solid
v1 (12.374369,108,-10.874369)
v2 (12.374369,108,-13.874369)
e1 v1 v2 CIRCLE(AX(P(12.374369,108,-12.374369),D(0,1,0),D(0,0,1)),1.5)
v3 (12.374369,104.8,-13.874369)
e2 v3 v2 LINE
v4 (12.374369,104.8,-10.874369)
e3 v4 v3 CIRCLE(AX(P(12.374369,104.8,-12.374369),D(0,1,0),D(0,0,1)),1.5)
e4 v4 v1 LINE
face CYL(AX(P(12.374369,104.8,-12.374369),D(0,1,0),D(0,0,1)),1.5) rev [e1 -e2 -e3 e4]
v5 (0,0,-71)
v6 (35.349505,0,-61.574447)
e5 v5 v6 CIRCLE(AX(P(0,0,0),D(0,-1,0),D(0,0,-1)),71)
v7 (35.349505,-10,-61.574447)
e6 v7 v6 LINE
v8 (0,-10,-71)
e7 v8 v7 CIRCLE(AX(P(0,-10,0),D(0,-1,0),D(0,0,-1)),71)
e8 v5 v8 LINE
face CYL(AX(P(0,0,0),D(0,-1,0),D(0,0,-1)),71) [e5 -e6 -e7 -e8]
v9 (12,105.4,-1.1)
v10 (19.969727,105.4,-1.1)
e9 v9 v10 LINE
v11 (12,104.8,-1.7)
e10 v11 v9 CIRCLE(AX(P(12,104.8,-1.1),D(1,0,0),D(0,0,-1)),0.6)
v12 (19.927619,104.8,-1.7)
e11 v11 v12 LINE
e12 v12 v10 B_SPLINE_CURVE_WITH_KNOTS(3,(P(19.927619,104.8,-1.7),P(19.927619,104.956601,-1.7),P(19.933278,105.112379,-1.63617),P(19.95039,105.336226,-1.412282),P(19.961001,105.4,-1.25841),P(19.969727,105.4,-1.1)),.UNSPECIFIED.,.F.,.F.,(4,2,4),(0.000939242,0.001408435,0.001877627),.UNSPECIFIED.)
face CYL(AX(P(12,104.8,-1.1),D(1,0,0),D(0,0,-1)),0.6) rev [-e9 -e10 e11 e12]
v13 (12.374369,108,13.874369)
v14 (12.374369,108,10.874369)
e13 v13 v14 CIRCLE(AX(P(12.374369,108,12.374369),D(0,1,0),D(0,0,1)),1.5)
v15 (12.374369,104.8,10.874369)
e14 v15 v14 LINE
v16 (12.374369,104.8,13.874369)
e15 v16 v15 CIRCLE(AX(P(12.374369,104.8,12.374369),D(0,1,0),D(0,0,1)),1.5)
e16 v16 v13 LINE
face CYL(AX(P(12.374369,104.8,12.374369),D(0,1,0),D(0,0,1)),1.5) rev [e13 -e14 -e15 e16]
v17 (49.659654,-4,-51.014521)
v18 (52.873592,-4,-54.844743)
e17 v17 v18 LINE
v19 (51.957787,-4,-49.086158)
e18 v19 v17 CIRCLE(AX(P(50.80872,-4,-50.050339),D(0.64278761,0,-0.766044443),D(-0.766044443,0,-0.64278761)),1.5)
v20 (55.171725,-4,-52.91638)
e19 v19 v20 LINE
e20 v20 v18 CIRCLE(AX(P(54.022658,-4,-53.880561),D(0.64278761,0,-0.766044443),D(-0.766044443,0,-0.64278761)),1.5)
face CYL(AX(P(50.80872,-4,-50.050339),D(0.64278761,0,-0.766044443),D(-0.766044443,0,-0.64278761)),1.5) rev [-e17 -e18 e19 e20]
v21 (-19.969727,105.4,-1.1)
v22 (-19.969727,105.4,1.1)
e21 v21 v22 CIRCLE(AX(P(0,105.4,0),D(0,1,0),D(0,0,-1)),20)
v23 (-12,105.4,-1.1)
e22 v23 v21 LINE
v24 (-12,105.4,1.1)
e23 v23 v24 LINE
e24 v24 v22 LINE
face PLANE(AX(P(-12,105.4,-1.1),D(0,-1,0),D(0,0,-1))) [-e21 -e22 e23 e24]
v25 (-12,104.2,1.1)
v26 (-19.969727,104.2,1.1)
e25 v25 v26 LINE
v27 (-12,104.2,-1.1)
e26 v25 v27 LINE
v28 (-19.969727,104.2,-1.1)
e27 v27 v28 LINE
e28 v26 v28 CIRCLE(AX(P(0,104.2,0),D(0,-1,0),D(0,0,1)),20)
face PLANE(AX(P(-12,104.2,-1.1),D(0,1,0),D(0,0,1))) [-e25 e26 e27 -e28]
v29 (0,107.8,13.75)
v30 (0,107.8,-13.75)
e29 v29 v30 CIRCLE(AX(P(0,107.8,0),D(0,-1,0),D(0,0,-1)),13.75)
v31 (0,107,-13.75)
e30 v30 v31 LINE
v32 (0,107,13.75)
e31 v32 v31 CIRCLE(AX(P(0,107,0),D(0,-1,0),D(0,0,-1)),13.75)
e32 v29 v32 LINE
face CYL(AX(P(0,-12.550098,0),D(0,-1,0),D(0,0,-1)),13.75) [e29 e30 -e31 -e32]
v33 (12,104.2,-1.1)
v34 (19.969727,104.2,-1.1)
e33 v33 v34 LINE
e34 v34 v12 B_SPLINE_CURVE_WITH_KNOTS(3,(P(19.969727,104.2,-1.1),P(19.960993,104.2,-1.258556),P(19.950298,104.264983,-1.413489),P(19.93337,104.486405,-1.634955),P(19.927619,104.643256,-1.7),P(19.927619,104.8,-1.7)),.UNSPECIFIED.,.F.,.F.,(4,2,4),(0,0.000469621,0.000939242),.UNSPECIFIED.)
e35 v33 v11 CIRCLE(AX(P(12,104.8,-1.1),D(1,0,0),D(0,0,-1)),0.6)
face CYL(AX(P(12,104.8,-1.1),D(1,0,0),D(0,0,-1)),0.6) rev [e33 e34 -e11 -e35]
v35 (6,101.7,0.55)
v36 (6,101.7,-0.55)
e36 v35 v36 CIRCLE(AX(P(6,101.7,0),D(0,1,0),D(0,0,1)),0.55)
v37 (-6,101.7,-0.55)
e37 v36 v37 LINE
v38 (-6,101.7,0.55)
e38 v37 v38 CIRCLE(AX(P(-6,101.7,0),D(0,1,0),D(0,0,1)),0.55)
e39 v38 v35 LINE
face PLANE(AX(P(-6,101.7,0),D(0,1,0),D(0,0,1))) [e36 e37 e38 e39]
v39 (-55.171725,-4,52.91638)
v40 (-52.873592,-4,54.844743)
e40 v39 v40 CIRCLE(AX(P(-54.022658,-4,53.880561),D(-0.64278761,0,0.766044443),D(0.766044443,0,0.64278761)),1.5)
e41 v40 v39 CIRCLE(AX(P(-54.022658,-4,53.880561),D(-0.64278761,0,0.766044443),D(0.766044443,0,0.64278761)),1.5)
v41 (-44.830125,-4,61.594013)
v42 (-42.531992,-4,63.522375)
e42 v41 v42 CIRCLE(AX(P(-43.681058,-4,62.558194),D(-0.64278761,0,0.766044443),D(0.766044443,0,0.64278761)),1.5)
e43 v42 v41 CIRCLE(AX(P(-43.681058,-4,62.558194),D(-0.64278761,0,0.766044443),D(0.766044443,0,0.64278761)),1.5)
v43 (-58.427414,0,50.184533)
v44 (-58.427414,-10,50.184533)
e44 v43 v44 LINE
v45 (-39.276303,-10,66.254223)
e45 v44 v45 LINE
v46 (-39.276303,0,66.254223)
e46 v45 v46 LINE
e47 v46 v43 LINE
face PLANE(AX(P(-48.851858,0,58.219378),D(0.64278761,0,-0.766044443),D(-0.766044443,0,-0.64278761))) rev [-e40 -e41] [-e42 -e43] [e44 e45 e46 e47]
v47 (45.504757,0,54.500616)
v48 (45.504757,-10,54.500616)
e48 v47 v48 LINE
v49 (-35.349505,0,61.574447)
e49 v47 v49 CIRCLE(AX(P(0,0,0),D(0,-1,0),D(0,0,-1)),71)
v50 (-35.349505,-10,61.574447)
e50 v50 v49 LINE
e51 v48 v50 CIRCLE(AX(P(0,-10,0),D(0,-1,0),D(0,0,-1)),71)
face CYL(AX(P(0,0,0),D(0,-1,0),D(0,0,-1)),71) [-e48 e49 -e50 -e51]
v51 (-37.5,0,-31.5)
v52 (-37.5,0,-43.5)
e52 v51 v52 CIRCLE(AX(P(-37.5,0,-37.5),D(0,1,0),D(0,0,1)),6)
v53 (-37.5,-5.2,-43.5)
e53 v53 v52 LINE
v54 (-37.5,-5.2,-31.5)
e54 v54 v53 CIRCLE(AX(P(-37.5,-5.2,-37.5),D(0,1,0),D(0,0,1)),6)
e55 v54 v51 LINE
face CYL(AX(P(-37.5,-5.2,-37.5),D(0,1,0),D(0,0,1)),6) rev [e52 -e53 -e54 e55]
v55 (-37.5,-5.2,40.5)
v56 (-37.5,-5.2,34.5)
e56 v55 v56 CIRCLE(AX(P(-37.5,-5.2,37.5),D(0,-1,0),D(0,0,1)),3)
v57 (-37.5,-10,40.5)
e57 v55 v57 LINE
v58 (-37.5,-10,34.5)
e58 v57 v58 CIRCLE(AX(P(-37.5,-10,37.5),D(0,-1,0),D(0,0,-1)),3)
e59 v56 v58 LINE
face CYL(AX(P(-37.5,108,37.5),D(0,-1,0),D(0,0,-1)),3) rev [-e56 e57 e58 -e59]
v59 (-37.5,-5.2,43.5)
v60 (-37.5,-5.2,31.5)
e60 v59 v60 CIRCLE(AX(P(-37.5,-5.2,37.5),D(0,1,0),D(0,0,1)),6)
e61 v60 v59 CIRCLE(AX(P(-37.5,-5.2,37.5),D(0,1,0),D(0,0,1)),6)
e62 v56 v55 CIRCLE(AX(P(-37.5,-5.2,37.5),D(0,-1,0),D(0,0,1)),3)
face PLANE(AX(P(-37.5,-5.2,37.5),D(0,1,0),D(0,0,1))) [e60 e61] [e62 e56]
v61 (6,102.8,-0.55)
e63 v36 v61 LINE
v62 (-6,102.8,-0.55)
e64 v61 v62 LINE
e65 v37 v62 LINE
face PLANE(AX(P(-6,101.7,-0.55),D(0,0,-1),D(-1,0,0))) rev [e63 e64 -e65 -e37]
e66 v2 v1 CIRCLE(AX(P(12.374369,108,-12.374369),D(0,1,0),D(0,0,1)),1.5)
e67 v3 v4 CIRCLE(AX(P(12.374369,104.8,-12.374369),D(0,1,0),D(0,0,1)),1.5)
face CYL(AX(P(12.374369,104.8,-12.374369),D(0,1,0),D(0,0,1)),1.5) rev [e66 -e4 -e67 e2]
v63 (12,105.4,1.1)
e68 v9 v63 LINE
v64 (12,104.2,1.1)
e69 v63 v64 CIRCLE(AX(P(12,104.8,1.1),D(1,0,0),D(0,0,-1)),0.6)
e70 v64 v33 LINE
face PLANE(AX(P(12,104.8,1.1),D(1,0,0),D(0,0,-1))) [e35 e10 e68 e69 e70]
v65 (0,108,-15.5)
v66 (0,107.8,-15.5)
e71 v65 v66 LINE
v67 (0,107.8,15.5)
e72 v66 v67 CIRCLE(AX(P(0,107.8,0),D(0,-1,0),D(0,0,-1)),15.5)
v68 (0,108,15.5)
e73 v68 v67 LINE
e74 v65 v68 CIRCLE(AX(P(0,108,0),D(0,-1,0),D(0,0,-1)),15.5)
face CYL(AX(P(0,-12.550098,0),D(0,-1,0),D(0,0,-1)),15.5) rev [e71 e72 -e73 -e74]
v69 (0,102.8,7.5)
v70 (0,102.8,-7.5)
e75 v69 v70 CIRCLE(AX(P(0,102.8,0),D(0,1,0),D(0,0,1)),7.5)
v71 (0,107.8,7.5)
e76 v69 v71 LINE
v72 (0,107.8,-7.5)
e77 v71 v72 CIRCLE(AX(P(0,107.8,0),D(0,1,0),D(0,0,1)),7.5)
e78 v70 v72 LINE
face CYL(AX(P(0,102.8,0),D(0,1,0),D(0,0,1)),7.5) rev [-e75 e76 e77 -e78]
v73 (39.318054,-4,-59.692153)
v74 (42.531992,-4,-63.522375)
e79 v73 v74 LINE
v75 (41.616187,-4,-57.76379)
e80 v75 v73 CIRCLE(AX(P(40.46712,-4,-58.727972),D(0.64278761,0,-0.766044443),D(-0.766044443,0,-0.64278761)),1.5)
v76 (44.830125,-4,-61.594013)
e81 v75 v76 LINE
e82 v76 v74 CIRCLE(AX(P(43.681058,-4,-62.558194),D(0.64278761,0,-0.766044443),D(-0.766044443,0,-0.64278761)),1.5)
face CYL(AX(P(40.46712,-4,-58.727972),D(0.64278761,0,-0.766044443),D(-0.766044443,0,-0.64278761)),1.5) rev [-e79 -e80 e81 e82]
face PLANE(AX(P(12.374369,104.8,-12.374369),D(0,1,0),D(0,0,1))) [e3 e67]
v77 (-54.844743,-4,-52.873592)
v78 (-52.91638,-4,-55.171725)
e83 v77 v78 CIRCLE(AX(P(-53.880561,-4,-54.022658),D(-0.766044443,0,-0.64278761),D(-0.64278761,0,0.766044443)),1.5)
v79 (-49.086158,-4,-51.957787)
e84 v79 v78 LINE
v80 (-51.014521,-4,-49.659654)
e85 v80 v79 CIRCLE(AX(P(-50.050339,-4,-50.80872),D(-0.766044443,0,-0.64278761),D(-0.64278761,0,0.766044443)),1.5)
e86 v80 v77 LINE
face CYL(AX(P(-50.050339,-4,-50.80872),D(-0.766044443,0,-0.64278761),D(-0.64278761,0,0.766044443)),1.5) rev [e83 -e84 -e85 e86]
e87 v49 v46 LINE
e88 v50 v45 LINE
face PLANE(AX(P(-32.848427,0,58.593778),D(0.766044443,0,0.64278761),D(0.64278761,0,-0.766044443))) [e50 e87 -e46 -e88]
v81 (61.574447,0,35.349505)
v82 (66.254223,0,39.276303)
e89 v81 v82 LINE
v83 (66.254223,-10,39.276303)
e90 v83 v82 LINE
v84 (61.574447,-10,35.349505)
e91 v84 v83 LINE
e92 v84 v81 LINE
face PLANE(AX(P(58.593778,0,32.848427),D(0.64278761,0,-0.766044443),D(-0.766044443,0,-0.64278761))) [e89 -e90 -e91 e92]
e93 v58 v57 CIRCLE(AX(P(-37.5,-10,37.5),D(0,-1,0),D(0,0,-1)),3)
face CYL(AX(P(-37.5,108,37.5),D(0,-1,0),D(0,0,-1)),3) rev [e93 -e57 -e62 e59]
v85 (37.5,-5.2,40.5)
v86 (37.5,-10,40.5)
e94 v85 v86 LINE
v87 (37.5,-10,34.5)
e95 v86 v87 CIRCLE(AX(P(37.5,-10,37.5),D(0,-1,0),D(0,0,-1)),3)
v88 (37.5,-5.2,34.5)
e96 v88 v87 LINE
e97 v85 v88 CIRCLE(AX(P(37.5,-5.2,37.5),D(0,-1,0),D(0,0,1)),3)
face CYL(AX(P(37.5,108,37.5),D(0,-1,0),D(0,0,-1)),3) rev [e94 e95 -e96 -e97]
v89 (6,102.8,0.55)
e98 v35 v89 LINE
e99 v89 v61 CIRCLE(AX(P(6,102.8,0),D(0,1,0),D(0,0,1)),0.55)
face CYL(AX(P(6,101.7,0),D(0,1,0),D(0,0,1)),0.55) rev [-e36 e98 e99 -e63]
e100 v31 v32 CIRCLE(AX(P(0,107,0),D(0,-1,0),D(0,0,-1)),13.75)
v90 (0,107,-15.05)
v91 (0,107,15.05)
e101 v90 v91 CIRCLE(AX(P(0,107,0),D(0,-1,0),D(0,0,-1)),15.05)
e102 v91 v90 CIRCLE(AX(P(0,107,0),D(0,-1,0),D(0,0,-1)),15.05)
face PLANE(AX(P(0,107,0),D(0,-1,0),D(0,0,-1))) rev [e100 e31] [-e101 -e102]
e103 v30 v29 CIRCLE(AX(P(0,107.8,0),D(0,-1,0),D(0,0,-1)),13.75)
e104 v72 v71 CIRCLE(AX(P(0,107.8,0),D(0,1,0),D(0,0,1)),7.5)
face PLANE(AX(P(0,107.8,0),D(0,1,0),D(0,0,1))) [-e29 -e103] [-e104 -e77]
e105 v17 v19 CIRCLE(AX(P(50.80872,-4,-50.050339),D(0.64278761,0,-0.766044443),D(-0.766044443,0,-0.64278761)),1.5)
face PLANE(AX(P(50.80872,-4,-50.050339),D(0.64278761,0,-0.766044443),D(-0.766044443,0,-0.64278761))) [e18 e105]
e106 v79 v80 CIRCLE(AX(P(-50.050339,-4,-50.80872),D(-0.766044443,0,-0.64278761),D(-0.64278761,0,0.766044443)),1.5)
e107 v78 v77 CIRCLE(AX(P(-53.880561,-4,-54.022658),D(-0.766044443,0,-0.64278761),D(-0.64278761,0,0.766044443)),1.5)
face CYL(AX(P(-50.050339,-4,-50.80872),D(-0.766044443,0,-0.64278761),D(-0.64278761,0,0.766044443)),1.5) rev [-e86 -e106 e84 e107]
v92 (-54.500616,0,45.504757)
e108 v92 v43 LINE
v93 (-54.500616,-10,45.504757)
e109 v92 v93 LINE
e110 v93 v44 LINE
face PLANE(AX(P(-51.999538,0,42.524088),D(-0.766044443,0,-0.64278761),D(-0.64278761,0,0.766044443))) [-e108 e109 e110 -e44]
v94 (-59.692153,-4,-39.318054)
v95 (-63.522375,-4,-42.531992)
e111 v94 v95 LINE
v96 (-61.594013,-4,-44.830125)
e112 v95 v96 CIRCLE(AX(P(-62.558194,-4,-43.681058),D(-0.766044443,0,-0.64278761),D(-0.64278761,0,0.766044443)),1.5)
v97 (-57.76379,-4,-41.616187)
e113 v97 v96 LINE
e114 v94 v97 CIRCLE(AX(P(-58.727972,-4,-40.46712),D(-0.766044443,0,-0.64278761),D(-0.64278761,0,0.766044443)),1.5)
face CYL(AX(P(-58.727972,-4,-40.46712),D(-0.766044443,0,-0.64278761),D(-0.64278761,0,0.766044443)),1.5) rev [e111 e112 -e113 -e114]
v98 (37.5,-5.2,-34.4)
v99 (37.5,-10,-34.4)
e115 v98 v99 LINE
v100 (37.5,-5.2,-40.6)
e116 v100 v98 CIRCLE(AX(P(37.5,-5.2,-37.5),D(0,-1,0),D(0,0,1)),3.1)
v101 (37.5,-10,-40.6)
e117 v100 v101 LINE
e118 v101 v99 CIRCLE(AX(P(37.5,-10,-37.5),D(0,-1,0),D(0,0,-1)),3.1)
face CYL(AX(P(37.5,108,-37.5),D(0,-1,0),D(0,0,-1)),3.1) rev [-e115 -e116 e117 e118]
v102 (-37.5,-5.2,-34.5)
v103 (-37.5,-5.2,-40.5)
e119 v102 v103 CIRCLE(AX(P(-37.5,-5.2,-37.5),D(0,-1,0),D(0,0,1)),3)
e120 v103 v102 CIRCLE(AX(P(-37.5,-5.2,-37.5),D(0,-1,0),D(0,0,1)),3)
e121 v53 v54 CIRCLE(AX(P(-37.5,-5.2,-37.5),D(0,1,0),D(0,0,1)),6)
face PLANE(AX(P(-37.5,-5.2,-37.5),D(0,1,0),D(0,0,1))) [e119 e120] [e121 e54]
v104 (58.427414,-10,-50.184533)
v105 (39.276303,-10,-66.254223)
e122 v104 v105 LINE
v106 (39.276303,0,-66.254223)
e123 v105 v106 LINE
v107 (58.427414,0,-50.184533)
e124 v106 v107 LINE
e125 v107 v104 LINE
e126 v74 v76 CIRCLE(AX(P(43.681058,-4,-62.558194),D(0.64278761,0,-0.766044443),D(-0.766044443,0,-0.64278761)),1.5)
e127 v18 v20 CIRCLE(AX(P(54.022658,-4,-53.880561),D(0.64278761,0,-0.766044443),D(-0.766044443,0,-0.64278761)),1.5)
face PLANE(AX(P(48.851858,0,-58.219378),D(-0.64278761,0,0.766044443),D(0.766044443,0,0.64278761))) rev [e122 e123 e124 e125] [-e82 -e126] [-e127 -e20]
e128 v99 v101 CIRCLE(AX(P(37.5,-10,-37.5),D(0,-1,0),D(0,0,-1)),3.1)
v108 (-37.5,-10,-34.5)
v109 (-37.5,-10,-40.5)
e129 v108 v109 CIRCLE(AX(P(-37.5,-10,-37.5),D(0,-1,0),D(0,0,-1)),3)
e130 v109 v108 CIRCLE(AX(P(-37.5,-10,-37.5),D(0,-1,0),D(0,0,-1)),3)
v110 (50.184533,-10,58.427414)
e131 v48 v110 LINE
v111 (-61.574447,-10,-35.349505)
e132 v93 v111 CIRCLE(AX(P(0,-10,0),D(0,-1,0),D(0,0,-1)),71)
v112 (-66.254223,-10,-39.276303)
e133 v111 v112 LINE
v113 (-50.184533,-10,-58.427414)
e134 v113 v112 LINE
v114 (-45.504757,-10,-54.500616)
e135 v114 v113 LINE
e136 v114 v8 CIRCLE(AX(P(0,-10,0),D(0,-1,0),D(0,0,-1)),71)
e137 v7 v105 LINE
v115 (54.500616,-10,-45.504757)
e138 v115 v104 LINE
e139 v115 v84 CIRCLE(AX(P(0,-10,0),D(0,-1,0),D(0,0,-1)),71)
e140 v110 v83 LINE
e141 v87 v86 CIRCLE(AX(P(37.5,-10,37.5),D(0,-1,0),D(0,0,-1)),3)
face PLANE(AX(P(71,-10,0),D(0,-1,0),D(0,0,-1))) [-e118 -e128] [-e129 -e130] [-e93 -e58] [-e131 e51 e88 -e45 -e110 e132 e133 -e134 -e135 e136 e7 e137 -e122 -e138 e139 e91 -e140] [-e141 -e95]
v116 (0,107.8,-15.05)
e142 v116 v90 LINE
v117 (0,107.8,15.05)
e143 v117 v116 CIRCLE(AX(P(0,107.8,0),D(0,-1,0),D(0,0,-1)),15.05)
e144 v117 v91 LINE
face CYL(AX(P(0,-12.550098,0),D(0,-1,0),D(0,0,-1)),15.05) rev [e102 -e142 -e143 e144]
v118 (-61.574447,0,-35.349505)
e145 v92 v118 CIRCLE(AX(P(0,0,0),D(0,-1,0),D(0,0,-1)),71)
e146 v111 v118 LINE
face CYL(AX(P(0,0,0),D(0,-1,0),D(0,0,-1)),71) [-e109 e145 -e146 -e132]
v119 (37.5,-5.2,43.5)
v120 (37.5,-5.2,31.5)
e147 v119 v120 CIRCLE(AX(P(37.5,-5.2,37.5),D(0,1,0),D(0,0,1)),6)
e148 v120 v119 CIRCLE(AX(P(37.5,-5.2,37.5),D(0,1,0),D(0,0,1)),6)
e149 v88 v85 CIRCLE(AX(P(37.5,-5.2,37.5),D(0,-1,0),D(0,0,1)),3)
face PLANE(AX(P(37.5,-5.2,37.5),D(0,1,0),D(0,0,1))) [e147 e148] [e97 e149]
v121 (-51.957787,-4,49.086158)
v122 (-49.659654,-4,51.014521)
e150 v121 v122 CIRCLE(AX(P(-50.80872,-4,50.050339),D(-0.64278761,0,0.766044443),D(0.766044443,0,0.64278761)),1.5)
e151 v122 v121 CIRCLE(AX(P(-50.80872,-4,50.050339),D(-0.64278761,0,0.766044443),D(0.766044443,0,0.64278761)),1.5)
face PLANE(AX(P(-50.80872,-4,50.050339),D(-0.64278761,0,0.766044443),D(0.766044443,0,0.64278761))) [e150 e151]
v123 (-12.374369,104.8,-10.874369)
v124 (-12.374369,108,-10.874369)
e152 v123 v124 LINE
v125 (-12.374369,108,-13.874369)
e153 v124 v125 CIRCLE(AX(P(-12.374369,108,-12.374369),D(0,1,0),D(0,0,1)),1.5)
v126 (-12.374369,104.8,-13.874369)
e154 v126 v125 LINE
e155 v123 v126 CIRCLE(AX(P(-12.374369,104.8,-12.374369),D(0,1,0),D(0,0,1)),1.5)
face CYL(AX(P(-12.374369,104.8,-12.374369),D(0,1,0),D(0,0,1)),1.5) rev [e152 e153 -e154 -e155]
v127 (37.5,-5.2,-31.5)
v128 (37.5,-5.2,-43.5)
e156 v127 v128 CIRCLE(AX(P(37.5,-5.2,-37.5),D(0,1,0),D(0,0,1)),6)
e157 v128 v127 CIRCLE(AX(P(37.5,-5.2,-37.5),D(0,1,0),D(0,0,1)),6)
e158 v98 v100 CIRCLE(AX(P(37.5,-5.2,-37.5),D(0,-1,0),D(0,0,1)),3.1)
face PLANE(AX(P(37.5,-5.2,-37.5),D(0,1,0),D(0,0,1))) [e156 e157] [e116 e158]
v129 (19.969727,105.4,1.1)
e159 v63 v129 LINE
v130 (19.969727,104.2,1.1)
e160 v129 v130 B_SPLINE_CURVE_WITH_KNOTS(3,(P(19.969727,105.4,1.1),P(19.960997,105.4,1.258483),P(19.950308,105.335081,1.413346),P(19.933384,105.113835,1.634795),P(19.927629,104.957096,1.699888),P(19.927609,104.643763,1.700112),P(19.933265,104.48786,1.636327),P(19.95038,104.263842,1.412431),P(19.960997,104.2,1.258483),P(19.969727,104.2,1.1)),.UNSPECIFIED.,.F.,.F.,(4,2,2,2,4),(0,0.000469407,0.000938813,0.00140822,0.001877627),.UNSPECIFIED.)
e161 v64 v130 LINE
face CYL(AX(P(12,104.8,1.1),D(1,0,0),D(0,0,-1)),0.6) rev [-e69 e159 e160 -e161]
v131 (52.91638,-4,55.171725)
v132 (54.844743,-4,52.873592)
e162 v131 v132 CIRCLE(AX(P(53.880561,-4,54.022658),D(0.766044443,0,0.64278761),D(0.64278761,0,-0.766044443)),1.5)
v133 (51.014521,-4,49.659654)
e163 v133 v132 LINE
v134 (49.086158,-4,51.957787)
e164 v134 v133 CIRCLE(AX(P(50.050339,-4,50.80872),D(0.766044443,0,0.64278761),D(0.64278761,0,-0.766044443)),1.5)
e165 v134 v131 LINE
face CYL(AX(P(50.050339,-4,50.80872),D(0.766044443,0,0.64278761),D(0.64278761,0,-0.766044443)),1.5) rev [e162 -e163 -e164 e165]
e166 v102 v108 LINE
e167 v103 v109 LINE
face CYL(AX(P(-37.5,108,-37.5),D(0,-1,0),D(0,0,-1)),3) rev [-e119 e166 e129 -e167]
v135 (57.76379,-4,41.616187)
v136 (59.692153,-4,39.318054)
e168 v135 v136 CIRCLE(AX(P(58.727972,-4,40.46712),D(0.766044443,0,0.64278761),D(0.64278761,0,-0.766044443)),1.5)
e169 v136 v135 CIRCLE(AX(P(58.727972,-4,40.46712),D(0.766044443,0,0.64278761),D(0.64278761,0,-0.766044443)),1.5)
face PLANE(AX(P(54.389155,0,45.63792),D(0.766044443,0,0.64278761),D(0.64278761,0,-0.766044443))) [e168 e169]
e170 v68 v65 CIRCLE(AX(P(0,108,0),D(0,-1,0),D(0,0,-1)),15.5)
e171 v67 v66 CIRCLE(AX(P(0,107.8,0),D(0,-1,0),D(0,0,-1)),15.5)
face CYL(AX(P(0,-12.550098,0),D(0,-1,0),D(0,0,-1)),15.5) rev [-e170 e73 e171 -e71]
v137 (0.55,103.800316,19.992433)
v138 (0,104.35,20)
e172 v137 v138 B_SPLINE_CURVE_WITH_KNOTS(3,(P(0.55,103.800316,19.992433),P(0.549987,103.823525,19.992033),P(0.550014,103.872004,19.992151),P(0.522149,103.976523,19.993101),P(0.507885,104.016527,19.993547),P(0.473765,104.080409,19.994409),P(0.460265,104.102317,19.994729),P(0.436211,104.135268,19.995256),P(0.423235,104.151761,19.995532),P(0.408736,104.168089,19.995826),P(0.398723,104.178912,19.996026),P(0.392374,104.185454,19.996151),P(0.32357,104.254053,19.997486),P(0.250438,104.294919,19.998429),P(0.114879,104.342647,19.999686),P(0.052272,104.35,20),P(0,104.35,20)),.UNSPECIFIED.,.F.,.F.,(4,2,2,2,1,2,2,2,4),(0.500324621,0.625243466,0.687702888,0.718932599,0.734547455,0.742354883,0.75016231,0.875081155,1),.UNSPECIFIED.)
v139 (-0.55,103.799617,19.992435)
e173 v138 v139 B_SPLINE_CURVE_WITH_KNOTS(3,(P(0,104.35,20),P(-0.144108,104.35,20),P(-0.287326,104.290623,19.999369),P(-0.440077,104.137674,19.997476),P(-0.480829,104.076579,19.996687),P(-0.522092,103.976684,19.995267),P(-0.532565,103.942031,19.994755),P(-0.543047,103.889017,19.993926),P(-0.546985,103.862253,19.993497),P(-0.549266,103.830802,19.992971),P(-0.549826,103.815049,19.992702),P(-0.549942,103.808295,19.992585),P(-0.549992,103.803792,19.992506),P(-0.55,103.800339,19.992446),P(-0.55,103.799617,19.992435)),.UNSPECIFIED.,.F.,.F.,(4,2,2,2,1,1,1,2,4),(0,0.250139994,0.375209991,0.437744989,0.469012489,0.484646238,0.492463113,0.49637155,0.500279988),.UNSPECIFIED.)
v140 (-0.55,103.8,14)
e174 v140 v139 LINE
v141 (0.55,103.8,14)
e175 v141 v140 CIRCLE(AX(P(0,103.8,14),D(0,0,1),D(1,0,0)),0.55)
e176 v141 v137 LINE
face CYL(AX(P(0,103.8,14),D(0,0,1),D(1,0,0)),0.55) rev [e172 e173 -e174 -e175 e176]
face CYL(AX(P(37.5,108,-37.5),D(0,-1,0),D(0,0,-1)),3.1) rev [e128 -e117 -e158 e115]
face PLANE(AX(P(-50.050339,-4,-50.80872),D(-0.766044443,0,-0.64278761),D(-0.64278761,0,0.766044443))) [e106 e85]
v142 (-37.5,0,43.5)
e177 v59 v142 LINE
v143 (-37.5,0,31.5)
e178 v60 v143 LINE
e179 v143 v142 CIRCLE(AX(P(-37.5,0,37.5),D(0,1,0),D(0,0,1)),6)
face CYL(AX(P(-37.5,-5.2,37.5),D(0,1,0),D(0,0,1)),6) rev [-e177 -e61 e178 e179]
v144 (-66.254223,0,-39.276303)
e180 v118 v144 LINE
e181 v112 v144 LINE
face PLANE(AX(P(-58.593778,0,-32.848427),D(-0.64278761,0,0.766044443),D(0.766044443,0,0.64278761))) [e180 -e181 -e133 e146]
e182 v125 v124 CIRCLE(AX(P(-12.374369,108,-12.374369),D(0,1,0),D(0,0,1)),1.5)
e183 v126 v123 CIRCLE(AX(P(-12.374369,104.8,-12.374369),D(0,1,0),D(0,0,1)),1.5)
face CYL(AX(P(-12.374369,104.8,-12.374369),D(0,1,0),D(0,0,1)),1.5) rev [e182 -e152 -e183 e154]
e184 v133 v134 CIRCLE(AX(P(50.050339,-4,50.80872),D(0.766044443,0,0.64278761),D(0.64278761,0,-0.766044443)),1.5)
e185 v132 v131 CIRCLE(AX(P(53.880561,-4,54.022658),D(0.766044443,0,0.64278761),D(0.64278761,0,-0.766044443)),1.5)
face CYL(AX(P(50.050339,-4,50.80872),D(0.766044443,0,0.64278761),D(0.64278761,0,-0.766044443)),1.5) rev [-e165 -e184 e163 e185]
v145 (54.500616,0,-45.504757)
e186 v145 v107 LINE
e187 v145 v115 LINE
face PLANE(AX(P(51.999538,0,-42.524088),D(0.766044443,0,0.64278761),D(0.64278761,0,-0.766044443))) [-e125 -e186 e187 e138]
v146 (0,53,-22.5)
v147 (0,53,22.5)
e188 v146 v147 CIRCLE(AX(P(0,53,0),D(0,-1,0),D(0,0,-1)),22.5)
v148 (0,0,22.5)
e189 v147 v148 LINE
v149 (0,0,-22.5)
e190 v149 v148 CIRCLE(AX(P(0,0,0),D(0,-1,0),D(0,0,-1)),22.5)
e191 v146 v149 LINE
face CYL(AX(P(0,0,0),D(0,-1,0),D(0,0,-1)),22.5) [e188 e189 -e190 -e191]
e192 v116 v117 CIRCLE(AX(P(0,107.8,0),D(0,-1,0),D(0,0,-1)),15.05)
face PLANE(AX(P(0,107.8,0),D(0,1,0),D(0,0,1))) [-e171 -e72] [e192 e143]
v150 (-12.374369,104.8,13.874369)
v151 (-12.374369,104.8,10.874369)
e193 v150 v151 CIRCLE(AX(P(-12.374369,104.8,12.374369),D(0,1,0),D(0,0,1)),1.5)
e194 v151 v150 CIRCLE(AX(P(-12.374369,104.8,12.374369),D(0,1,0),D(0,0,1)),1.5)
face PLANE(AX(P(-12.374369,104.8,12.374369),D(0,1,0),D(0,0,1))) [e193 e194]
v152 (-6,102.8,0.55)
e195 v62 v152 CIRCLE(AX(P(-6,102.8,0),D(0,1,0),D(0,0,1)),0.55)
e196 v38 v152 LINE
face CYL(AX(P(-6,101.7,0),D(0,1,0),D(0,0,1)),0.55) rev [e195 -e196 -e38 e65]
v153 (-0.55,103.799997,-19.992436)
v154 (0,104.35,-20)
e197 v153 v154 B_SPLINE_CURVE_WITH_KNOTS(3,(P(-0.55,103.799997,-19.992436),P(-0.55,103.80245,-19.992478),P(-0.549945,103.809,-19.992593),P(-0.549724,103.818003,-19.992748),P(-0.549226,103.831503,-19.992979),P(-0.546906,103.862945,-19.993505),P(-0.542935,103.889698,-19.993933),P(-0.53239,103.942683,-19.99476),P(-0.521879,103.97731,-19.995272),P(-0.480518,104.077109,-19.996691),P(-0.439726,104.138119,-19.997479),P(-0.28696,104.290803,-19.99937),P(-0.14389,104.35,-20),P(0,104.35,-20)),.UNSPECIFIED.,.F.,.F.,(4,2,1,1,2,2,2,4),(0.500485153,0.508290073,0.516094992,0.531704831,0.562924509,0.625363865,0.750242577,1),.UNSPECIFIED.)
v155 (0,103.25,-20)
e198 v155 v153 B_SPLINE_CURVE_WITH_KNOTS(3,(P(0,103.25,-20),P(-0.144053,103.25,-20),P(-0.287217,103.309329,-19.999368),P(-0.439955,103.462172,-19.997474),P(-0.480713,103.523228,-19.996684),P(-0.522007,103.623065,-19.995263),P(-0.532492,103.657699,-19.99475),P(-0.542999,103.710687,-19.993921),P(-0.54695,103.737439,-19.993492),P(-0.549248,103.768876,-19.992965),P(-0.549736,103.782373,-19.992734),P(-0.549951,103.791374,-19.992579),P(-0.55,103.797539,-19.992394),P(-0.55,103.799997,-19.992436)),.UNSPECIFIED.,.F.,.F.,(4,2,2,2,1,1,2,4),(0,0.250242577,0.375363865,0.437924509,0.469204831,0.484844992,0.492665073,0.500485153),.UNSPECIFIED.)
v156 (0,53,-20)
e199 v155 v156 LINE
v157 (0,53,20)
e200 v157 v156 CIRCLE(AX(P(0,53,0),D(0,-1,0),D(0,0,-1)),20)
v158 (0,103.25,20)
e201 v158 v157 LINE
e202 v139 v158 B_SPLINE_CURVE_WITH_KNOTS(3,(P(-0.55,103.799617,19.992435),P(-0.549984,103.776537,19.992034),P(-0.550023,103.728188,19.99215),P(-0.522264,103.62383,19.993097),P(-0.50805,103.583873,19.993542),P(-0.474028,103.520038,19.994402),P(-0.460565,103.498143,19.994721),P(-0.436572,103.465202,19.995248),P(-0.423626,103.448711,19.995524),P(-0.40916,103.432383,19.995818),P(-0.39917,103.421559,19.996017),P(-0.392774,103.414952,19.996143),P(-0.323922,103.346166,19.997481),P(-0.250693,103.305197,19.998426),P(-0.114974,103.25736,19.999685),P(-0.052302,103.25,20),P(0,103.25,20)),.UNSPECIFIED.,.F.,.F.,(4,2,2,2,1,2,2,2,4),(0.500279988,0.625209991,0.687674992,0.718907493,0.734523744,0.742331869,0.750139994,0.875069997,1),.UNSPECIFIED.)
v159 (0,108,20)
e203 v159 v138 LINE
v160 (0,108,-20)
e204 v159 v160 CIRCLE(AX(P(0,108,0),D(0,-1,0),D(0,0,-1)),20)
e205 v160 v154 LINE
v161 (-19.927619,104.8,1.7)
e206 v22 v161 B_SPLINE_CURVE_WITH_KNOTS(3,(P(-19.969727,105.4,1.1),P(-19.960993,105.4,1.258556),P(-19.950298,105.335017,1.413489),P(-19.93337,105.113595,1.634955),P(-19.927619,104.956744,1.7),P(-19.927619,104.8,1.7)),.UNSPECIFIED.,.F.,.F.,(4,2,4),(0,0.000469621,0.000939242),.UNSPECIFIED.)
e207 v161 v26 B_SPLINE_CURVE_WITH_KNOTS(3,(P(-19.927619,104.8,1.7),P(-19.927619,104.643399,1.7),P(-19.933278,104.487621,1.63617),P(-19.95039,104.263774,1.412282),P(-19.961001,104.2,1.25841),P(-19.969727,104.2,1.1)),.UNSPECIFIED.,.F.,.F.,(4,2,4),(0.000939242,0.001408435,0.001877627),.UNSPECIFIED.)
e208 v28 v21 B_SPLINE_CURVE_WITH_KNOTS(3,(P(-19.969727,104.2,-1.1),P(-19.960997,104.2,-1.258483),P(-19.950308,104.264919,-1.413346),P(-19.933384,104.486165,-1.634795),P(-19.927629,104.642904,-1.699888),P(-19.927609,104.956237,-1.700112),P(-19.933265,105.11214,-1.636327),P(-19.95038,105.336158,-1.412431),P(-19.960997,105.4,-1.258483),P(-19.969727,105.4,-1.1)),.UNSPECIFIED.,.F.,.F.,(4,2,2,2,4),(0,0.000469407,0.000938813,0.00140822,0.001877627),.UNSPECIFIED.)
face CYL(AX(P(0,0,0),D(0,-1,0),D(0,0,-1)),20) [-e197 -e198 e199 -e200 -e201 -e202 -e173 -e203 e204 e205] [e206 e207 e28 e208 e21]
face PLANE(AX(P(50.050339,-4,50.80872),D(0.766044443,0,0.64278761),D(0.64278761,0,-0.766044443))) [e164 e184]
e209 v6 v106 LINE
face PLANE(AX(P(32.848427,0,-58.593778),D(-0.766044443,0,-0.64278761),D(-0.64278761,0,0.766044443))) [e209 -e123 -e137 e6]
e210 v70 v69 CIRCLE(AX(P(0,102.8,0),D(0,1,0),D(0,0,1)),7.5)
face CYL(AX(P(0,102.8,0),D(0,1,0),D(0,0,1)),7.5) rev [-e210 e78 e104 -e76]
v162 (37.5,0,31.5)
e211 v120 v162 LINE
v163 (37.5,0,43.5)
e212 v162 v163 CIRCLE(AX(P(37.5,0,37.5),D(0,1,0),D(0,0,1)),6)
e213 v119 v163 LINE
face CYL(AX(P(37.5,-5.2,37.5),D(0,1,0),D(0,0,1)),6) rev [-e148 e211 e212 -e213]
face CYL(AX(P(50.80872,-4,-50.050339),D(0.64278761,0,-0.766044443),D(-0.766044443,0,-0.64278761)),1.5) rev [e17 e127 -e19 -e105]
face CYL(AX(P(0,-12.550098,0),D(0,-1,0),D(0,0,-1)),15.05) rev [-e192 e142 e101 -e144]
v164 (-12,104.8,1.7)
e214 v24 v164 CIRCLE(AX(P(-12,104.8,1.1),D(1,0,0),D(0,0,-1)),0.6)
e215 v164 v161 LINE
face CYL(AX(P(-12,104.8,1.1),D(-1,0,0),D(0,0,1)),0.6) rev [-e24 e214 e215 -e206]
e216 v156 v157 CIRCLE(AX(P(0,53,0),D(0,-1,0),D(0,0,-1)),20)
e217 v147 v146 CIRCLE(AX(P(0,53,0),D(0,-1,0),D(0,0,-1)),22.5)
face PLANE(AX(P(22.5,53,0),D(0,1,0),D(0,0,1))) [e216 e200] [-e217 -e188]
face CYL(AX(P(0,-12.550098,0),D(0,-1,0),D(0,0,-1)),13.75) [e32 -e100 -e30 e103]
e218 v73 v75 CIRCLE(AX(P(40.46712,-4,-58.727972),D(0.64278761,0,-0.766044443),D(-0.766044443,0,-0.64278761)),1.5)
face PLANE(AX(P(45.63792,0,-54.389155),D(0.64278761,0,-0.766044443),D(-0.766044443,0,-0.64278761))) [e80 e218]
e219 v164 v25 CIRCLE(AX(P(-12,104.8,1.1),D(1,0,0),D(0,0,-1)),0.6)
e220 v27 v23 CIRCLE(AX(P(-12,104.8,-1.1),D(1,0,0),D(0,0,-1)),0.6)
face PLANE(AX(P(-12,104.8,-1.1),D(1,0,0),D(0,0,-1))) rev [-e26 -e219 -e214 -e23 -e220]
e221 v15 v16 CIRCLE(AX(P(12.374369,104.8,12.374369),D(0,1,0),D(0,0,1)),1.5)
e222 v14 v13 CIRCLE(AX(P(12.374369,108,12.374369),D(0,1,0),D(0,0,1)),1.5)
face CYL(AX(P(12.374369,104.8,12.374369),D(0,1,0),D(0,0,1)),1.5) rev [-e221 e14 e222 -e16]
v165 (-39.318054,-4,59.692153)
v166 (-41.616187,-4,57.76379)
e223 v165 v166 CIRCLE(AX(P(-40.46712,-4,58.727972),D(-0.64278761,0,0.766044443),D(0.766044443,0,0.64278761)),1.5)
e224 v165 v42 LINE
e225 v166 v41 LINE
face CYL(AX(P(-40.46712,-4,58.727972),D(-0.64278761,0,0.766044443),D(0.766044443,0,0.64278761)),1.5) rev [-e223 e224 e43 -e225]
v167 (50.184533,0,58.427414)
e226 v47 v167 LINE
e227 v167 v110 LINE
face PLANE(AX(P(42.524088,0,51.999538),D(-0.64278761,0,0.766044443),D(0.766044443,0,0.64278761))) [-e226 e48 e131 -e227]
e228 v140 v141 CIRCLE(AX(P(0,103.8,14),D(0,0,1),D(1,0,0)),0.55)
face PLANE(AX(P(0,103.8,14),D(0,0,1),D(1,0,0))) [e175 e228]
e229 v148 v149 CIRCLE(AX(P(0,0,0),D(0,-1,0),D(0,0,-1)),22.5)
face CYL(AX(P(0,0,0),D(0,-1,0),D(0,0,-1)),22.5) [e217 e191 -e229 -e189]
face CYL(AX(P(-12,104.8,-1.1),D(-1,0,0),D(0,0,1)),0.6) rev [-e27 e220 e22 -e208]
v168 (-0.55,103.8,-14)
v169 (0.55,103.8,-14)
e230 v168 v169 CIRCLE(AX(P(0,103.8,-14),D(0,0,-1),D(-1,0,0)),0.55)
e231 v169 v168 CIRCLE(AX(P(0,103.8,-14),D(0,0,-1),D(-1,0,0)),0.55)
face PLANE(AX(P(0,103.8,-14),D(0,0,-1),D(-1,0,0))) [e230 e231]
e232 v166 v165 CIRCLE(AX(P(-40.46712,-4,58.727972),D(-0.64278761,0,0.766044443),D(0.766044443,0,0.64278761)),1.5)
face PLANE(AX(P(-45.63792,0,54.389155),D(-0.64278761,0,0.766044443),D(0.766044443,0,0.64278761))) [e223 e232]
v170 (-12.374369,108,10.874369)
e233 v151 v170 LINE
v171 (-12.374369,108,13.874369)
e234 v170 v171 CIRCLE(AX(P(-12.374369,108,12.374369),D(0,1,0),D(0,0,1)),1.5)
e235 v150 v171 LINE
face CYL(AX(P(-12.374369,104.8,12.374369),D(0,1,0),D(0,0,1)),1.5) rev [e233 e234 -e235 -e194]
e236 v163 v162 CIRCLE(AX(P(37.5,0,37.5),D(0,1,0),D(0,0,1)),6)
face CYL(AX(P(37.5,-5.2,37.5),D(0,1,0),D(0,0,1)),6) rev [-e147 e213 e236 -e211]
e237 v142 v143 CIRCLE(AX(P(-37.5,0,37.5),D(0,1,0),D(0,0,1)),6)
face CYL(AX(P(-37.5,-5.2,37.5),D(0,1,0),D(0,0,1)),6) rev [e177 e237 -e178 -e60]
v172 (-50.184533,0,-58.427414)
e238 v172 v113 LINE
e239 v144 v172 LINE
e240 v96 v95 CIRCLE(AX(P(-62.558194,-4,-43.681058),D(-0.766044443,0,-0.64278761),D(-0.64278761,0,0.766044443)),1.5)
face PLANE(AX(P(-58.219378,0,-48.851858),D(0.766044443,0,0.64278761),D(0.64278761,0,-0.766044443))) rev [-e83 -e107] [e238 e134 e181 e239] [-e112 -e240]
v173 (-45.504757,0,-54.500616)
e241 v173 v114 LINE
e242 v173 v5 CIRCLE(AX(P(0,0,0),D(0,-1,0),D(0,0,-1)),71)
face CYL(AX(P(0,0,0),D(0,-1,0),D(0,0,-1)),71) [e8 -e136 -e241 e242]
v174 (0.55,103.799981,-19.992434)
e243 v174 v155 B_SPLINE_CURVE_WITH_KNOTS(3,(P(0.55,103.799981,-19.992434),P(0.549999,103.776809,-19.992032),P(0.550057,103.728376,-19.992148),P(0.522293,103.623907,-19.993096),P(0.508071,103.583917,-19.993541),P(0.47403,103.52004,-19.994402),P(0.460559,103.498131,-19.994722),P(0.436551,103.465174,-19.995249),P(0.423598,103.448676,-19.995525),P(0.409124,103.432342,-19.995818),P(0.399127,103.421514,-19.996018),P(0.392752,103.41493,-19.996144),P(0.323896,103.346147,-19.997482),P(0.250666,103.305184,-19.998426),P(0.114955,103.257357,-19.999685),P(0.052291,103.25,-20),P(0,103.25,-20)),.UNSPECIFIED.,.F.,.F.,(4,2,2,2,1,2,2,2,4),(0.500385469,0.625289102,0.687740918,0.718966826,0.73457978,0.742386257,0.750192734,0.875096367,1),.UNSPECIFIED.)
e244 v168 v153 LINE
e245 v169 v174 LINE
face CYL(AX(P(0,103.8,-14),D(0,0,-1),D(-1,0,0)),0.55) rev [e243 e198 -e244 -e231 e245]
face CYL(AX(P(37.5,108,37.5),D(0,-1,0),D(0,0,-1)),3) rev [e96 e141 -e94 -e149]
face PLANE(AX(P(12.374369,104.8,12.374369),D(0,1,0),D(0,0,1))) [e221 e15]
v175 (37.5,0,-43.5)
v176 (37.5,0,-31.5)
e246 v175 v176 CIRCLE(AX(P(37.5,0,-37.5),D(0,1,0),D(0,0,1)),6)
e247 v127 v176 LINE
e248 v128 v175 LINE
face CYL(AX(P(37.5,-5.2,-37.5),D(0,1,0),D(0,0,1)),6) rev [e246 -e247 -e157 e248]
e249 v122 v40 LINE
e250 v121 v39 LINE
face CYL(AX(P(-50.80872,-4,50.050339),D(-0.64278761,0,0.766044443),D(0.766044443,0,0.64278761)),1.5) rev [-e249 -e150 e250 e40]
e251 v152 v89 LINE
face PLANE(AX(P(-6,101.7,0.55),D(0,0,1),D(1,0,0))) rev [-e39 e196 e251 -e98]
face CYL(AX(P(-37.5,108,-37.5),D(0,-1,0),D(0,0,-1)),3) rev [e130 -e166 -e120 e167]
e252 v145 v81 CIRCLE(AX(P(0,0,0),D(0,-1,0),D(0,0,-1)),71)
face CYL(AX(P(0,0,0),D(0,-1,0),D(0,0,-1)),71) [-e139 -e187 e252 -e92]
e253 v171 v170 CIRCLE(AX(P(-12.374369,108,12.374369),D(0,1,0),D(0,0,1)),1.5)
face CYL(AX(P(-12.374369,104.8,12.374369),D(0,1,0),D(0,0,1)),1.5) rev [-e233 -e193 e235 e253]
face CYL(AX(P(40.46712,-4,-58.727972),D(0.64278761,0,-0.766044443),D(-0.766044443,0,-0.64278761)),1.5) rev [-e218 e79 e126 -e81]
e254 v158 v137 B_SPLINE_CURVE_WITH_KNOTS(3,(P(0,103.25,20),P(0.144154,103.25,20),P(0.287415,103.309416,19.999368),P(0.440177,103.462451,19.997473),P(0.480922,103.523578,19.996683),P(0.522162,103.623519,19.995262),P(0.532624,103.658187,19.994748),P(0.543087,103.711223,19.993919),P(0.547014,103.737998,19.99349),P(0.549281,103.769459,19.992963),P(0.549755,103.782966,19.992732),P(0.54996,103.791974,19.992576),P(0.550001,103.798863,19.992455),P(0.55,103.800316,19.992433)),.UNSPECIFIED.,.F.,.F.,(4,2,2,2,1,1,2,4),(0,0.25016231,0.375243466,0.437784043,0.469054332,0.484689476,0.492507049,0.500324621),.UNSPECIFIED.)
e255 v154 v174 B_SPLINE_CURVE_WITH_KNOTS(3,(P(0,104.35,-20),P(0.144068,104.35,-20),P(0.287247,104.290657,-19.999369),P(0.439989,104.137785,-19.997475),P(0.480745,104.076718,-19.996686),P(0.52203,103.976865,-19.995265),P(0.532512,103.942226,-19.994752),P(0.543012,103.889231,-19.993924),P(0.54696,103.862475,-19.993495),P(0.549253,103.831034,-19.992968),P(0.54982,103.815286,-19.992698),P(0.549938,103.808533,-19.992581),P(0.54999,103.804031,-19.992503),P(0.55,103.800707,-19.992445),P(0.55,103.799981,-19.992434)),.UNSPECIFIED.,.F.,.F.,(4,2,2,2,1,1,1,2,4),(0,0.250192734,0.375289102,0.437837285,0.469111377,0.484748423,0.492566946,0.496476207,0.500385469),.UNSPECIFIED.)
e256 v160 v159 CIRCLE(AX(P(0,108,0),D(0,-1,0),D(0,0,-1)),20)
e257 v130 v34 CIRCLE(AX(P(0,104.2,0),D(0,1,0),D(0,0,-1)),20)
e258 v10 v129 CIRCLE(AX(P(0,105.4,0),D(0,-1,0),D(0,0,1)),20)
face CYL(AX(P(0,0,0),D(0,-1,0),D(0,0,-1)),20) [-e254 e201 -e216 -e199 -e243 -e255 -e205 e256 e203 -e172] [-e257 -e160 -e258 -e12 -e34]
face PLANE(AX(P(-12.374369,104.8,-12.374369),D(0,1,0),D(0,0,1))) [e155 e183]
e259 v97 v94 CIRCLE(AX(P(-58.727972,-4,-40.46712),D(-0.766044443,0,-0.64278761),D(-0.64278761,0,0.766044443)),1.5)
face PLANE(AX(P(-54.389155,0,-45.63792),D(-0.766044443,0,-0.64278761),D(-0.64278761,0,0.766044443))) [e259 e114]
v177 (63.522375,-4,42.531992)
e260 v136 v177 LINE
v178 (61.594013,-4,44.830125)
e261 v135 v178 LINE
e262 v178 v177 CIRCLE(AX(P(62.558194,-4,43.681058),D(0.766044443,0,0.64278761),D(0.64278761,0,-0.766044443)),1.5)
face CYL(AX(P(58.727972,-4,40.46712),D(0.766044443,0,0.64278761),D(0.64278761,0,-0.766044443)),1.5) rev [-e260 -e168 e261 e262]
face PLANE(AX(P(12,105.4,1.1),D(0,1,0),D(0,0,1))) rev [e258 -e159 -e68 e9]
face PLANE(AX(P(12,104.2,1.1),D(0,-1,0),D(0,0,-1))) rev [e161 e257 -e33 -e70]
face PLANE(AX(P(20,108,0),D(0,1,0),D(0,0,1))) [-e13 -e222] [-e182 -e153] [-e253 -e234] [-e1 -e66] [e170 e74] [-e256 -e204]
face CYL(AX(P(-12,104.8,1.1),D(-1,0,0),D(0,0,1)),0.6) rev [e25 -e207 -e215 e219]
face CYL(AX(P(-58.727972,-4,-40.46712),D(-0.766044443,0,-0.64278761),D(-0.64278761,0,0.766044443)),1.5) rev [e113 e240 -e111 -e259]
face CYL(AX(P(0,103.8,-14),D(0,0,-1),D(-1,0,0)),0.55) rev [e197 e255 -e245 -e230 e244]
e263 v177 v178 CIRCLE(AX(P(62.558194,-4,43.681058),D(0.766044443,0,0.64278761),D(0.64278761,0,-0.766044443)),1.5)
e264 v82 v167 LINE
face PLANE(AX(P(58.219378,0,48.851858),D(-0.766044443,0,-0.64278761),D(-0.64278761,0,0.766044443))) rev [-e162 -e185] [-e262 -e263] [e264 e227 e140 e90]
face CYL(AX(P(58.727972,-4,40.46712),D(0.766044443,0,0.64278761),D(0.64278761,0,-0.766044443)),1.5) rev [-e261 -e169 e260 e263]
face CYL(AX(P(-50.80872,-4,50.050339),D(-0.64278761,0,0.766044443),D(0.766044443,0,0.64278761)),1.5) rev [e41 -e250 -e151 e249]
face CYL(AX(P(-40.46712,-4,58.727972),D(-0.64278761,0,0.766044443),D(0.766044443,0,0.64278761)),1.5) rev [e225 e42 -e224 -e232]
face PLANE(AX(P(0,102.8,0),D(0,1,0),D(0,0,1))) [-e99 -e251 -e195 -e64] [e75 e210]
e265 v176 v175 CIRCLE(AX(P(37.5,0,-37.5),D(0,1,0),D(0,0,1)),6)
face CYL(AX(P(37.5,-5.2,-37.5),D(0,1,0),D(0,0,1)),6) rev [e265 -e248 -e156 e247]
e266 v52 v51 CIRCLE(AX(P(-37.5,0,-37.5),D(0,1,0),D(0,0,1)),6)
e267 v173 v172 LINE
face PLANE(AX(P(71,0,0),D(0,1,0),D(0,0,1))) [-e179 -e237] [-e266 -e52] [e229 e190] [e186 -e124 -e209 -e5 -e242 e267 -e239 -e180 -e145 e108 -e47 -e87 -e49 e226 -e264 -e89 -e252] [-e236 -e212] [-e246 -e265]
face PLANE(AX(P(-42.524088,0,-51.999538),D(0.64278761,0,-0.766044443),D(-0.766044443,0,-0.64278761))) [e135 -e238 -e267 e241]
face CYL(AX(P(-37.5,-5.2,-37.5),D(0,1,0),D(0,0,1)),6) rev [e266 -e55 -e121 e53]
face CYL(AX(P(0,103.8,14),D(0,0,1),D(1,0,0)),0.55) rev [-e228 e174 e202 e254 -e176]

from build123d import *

# Parameters (mm, degrees)
SKETCH4_R           = 7.5
CUT_EXTRUDE1_DEPTH  = 5
SKETCH8_R           = 1.5
CUT_EXTRUDE6_DEPTH  = 3
CUT_EXTRUDE15_DEPTH = 8
CUT_EXTRUDE8_START  = 8
CUT_EXTRUDE8_DEPTH  = 8
BOSS_EXTRUDE3_START = 71
SKETCH16_W          = 10
SKETCH16_H          = 25
BOSS_EXTRUDE3_DEPTH = 5
SKETCH17_R          = 1.5
CUT_EXTRUDE10_DEPTH = 5
CIRPATTERN2_COUNT   = 4
SKETCH21_R          = 3.1
SKETCH21_R_2        = 3
CUT_EXTRUDE12_DEPTH = 155.938697631
SKETCH22_R          = 6
CUT_EXTRUDE13_DEPTH = 5.2
SKETCH25_R          = 0.55
CUT_EXTRUDE16_DEPTH = 6
CUT_EXTRUDE17_START = -6
SKETCH27_R          = 0.55
CUT_EXTRUDE17_DEPTH = 6
CUT_EXTRUDE19_DEPTH = 1.1


with BuildPart() as part:
    # Sketch1 → Revolve1 (revolve)
    with BuildSketch(Plane.XY, mode=Mode.PRIVATE) as revolve1_sk:
        Polygon((22.5, 0), (22.5, 53), (20, 53), (20, 108), (0, 108), (0, 0), (0, -10), (71, -10), (71, 0), align=None)
    revolve(revolve1_sk.sketch.rotate(Axis((0, 0, 0), (0, 1, 0)), 90), axis=Axis((0, 0, 0), (0, 1, 0)))

    # Sketch3 → Cut-Revolve1 (revolve, cut)
    with BuildSketch(Plane.XY, mode=Mode.PRIVATE) as cut_revolve1_sk:
        Polygon((0, 108), (0, 107.8), (13.75, 107.8), (13.75, 107), (15.05, 107), (15.05, 107.8), (15.5, 107.8), (15.5, 108), align=None)
    revolve(cut_revolve1_sk.sketch.rotate(Axis((0, -12.550098123, 0), (0, 1, 0)), 90), axis=Axis((0, -12.550098123, 0), (0, 1, 0)), mode=Mode.SUBTRACT)

    # Sketch4 → Cut-Extrude1 (cut)
    with BuildSketch(Plane(origin=(0, 107.8, 0), x_dir=(1, 0, 0), z_dir=(0, 1, 0))):
        with Locations(Location((0, 0, 0), (0, 0, 270))):
            Circle(SKETCH4_R)
    extrude(amount=-CUT_EXTRUDE1_DEPTH, mode=Mode.SUBTRACT)

    # Sketch8 → Cut-Extrude6 (cut, symmetric)
    with BuildSketch(Plane(origin=(0, 107.8, 0), x_dir=(1, 0, 0), z_dir=(0, 1, 0))):
        with Locations(Location((12.374368671, 12.374368671, 0), (0, 0, 270))):
            Circle(SKETCH8_R)
        with Locations(Location((12.374368671, -12.374368671, 0), (0, 0, 270))):
            Circle(SKETCH8_R)
        with Locations(Location((-12.374368671, -12.374368671, 0), (0, 0, 270))):
            Circle(SKETCH8_R)
        with Locations(Location((-12.374368671, 12.374368671, 0), (0, 0, 270))):
            Circle(SKETCH8_R)
    extrude(amount=CUT_EXTRUDE6_DEPTH, both=True, mode=Mode.SUBTRACT)

    # Sketch24 → Cut-Extrude15 (cut)
    with BuildSketch(Plane(origin=(20, 0, 0), x_dir=(0, 0, -1), z_dir=(1, 0, 0))):
        with BuildLine():
            Line((-1.1, 105.4), (1.1, 105.4))
            ThreePointArc((1.1, 105.4), (1.7, 104.8), (1.1, 104.2))
            Line((1.1, 104.2), (-1.1, 104.2))
            ThreePointArc((-1.1, 104.2), (-1.7, 104.8), (-1.1, 105.4))
        make_face()
    extrude(amount=-CUT_EXTRUDE15_DEPTH, mode=Mode.SUBTRACT)

    # Sketch10 → Cut-Extrude8 (cut)
    with BuildSketch(Plane(origin=(-20, 0, 0), x_dir=(0, 0, -1), z_dir=(1, 0, 0)).offset(CUT_EXTRUDE8_START)):
        with BuildLine():
            Line((1.1, 104.2), (-1.1, 104.2))
            ThreePointArc((-1.1, 104.2), (-1.7, 104.8), (-1.1, 105.4))
            Line((-1.1, 105.4), (1.1, 105.4))
            ThreePointArc((1.1, 105.4), (1.7, 104.8), (1.1, 104.2))
        make_face()
    extrude(amount=-CUT_EXTRUDE8_DEPTH, mode=Mode.SUBTRACT)

    # Sketch16 → Boss-Extrude3 (add, symmetric)
    with BuildSketch(Plane(origin=(0, 0, 0), x_dir=(0, -1, 0), z_dir=(-0.6427876096865403, 0, 0.7660444431189772)).offset(BOSS_EXTRUDE3_START)):
        with Locations((5, 0)):
            Rectangle(SKETCH16_W, SKETCH16_H)
    boss_extrude3 = extrude(amount=BOSS_EXTRUDE3_DEPTH, both=True)

    # Sketch17 → Cut-Extrude10 (cut)
    with BuildSketch(Plane(origin=(-48.851858336, 0, 58.219377677), x_dir=(0.7660444431189771, 0, 0.6427876096865404), z_dir=(-0.6427876096865404, 0, 0.7660444431189771))):
        with Locations((6.75, -4)):
            Circle(SKETCH17_R)
        with Locations((-6.75, -4)):
            Circle(SKETCH17_R)
    cut_extrude10 = extrude(amount=-CUT_EXTRUDE10_DEPTH, mode=Mode.SUBTRACT)

    # CirPattern2: Boss-Extrude3, Cut-Extrude10 ×4 about axis
    cirpattern2_axis = Axis((0, 0, 0), (0, 1, 0))
    add([boss_extrude3.rotate(cirpattern2_axis, i * 360 / CIRPATTERN2_COUNT) for i in range(1, CIRPATTERN2_COUNT)])
    add([cut_extrude10.rotate(cirpattern2_axis, i * 360 / CIRPATTERN2_COUNT) for i in range(1, CIRPATTERN2_COUNT)], mode=Mode.SUBTRACT)

    # Sketch21 → Cut-Extrude12 (cut, through all)
    with BuildSketch(Plane(origin=(0, -10, 0), x_dir=(-1, 0, 0), z_dir=(0, -1, 0))):
        with Locations(Location((-37.5, 37.5, 0), (0, 0, 90))):
            Circle(SKETCH21_R)
        with Locations(Location((37.5, 37.5, 0), (0, 0, 90))):
            Circle(SKETCH21_R_2)
        with Locations(Location((-37.5, -37.5, 0), (0, 0, 90))):
            Circle(SKETCH21_R_2)
        with Locations(Location((37.5, -37.5, 0), (0, 0, 90))):
            Circle(SKETCH21_R_2)
    extrude(amount=-CUT_EXTRUDE12_DEPTH, mode=Mode.SUBTRACT)

    # Sketch22 → Cut-Extrude13 (cut)
    with BuildSketch(Plane(origin=(0, 0, 0), x_dir=(1, 0, 0), z_dir=(0, 1, 0))):
        with Locations(Location((-37.5, 37.5, 0), (0, 0, 270))):
            Circle(SKETCH22_R)
        with Locations(Location((37.5, 37.5, 0), (0, 0, 270))):
            Circle(SKETCH22_R)
        with Locations(Location((-37.5, -37.5, 0), (0, 0, 270))):
            Circle(SKETCH22_R)
        with Locations(Location((37.5, -37.5, 0), (0, 0, 270))):
            Circle(SKETCH22_R)
    extrude(amount=-CUT_EXTRUDE13_DEPTH, mode=Mode.SUBTRACT)

    # Sketch25 → Cut-Extrude16 (cut)
    with BuildSketch(Plane(origin=(0, 0, -20), x_dir=(-1, 0, 0), z_dir=(0, 0, -1))):
        with Locations((0, 103.8)):
            Circle(SKETCH25_R)
    extrude(amount=-CUT_EXTRUDE16_DEPTH, mode=Mode.SUBTRACT)

    # Sketch27 → Cut-Extrude17 (cut)
    with BuildSketch(Plane.XY.offset(20).offset(CUT_EXTRUDE17_START)):
        with Locations(Location((0, 103.8, 0), (0, 0, 180))):
            Circle(SKETCH27_R)
    extrude(amount=CUT_EXTRUDE17_DEPTH, mode=Mode.SUBTRACT)

    # Sketch28 → Cut-Extrude19 (cut)
    with BuildSketch(Plane(origin=(0, 102.8, 0), x_dir=(1, 0, 0), z_dir=(0, 1, 0))):
        with BuildLine():
            Line((-6, 0.55), (6, 0.55))
            ThreePointArc((6, 0.55), (6.55, 0), (6, -0.55))
            Line((6, -0.55), (-6, -0.55))
            ThreePointArc((-6, -0.55), (-6.55, 0), (-6, 0.55))
        make_face()
    extrude(amount=-CUT_EXTRUDE19_DEPTH, mode=Mode.SUBTRACT)


solid = part.part
